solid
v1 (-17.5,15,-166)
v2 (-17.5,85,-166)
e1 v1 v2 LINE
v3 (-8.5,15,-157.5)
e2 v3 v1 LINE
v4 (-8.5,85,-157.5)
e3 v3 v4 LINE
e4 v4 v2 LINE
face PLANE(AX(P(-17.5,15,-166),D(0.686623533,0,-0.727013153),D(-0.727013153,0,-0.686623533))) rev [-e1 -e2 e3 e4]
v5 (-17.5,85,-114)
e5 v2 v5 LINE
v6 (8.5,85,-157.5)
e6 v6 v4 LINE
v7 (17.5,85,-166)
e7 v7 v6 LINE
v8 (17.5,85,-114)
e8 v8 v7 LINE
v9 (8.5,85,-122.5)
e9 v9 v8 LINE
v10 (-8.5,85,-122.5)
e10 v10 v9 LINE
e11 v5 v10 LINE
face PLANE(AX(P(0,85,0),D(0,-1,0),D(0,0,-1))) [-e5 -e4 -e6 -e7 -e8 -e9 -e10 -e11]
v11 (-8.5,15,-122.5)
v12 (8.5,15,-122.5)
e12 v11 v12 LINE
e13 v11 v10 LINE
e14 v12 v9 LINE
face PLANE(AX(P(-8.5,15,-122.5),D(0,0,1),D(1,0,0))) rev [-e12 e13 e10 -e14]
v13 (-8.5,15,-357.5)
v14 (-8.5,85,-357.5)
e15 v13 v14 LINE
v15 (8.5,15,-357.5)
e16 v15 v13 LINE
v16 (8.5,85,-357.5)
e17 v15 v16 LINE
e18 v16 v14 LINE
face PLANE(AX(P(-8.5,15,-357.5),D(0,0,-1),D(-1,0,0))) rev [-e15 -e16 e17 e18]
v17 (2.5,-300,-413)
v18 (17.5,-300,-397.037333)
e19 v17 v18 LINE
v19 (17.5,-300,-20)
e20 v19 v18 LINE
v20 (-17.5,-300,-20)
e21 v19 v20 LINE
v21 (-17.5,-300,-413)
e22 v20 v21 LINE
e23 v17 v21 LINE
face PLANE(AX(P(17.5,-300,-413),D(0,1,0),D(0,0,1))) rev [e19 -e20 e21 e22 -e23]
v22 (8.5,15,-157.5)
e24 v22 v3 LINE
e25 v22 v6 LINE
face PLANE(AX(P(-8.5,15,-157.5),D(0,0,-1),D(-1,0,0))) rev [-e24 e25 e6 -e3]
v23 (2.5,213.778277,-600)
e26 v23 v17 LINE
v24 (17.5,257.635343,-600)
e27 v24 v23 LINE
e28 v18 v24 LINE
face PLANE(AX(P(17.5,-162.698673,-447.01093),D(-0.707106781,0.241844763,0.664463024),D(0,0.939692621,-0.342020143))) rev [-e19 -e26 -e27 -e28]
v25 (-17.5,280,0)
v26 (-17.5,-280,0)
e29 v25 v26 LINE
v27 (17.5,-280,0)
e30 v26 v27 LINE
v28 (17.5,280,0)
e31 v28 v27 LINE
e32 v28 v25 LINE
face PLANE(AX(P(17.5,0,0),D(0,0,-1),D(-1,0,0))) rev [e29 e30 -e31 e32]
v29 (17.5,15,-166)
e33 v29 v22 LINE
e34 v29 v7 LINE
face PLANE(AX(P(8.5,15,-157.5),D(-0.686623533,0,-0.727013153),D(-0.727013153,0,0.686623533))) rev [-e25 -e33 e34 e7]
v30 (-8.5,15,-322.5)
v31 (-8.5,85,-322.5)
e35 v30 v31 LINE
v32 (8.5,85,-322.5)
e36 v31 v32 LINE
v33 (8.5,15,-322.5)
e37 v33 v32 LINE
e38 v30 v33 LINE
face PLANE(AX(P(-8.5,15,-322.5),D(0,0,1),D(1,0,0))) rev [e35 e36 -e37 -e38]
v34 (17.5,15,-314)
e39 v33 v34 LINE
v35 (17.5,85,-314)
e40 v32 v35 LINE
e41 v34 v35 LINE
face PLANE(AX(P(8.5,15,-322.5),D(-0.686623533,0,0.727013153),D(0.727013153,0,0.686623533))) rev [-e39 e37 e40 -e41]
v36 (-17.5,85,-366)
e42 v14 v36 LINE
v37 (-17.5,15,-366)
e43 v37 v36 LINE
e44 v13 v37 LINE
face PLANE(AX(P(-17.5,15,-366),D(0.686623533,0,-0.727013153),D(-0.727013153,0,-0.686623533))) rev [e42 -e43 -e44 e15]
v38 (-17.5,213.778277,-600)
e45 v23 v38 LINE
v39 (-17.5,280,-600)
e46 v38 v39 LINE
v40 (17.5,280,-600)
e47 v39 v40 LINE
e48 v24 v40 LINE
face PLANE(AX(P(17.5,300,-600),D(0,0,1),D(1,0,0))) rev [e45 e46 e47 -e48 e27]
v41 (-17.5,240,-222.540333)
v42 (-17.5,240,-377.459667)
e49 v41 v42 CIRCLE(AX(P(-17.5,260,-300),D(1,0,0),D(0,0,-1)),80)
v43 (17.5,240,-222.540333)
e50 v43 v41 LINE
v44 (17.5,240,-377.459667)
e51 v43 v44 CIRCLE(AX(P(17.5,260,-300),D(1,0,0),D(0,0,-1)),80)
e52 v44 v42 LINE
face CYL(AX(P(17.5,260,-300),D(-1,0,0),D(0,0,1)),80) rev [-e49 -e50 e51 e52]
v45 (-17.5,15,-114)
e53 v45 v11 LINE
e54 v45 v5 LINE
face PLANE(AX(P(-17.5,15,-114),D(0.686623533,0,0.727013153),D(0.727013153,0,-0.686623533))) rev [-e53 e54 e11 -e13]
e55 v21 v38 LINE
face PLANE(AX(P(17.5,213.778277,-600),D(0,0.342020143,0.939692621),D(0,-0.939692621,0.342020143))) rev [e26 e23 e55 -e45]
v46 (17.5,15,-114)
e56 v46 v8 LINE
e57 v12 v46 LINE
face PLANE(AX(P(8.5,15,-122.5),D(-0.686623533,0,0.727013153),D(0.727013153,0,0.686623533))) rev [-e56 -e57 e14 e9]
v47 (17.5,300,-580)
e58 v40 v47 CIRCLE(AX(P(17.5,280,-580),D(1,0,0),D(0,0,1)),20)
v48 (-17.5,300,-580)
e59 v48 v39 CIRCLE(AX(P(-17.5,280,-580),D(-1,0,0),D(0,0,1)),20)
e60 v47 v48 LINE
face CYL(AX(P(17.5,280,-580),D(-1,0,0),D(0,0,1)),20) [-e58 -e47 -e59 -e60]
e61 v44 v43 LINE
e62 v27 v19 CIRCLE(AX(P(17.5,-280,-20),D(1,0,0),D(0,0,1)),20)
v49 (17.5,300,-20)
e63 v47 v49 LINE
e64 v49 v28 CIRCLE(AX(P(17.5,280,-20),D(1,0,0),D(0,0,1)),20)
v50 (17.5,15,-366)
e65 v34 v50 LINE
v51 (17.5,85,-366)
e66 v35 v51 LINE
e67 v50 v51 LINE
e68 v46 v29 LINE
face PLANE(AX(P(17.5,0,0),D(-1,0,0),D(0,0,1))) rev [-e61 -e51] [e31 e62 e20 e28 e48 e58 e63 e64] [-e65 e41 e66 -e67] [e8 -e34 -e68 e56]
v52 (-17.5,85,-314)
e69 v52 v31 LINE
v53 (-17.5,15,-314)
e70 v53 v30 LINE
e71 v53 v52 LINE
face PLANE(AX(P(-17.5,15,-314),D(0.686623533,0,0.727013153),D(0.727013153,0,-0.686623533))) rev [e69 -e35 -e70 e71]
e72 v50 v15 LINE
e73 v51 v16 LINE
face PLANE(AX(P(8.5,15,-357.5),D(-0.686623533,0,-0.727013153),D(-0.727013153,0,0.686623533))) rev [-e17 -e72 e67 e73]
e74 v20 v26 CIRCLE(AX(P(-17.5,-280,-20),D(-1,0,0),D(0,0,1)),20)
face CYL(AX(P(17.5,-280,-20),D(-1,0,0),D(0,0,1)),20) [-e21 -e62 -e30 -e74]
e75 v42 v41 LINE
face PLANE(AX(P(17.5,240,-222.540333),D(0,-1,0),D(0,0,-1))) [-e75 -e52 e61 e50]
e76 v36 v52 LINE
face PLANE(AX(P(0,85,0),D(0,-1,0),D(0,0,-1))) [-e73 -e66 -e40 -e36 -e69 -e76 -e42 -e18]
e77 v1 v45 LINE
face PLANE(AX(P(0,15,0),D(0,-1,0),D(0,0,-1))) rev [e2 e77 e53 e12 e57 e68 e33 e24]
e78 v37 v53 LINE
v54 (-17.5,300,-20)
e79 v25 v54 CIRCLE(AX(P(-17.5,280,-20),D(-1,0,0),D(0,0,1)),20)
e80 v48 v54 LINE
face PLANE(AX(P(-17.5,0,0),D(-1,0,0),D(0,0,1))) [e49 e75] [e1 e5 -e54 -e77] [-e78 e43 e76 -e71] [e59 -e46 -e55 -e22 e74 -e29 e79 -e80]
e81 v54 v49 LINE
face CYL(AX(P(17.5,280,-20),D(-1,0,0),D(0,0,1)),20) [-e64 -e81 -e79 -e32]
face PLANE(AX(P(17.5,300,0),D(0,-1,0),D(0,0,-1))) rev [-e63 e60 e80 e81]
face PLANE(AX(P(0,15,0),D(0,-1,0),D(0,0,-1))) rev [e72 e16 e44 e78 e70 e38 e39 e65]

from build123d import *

# Parameters (mm, degrees)
BOSS_EXTRUDE1_DEPTH = 17.5
CUT_EXTRUDE1_START  = 50
CUT_EXTRUDE1_DEPTH  = 35
FILLET1_R           = 20
CHAMFER2_SIZE       = 15


with BuildPart() as part:
    # Sketch1 → Boss-Extrude1 (new, symmetric)
    with BuildSketch(Plane(origin=(0, 0, 0), x_dir=(0, 0, -1), z_dir=(1, 0, 0))):
        Polygon((0, 0), (0, 300), (600, 300), (600, 213.778277438), (413, -300), (0, -300), align=None)
        with BuildLine():
            Line((222.540333076, 240), (377.459666924, 240))
            ThreePointArc((377.459666924, 240), (300, 180), (222.540333076, 240))
        make_face(mode=Mode.SUBTRACT)
    extrude(amount=BOSS_EXTRUDE1_DEPTH, both=True)

    # Sketch2 → Cut-Extrude1 (cut, symmetric)
    with BuildSketch(Plane(origin=(0, 0, 0), x_dir=(1, 0, 0), z_dir=(0, 1, 0)).offset(CUT_EXTRUDE1_START)):
        Polygon((-17.5, 114), (-8.5, 122.5), (8.5, 122.5), (17.5, 114), (17.5, 166), (8.5, 157.5), (-8.5, 157.5), (-17.5, 166), align=None)
        Polygon((8.5, 357.5), (17.5, 366), (17.5, 314), (8.5, 322.5), (-8.5, 322.5), (-17.5, 314), (-17.5, 366), (-8.5, 357.5), align=None)
    extrude(amount=CUT_EXTRUDE1_DEPTH, both=True, mode=Mode.SUBTRACT)

    # Fillet1
    fillet1_edges = [part.edges().sort_by_distance(p)[0] for p in [
        (0, 300, 0),
        (0, 300, -600),
        (0, -300, 0),
    ]]
    fillet(fillet1_edges, radius=FILLET1_R)

    # Chamfer2
    chamfer2_edges = [part.edges().sort_by_distance(p)[0] for p in [
        (17.5, -43.110861281, -506.5),
    ]]
    chamfer(chamfer2_edges, length=CHAMFER2_SIZE)


solid = part.part
